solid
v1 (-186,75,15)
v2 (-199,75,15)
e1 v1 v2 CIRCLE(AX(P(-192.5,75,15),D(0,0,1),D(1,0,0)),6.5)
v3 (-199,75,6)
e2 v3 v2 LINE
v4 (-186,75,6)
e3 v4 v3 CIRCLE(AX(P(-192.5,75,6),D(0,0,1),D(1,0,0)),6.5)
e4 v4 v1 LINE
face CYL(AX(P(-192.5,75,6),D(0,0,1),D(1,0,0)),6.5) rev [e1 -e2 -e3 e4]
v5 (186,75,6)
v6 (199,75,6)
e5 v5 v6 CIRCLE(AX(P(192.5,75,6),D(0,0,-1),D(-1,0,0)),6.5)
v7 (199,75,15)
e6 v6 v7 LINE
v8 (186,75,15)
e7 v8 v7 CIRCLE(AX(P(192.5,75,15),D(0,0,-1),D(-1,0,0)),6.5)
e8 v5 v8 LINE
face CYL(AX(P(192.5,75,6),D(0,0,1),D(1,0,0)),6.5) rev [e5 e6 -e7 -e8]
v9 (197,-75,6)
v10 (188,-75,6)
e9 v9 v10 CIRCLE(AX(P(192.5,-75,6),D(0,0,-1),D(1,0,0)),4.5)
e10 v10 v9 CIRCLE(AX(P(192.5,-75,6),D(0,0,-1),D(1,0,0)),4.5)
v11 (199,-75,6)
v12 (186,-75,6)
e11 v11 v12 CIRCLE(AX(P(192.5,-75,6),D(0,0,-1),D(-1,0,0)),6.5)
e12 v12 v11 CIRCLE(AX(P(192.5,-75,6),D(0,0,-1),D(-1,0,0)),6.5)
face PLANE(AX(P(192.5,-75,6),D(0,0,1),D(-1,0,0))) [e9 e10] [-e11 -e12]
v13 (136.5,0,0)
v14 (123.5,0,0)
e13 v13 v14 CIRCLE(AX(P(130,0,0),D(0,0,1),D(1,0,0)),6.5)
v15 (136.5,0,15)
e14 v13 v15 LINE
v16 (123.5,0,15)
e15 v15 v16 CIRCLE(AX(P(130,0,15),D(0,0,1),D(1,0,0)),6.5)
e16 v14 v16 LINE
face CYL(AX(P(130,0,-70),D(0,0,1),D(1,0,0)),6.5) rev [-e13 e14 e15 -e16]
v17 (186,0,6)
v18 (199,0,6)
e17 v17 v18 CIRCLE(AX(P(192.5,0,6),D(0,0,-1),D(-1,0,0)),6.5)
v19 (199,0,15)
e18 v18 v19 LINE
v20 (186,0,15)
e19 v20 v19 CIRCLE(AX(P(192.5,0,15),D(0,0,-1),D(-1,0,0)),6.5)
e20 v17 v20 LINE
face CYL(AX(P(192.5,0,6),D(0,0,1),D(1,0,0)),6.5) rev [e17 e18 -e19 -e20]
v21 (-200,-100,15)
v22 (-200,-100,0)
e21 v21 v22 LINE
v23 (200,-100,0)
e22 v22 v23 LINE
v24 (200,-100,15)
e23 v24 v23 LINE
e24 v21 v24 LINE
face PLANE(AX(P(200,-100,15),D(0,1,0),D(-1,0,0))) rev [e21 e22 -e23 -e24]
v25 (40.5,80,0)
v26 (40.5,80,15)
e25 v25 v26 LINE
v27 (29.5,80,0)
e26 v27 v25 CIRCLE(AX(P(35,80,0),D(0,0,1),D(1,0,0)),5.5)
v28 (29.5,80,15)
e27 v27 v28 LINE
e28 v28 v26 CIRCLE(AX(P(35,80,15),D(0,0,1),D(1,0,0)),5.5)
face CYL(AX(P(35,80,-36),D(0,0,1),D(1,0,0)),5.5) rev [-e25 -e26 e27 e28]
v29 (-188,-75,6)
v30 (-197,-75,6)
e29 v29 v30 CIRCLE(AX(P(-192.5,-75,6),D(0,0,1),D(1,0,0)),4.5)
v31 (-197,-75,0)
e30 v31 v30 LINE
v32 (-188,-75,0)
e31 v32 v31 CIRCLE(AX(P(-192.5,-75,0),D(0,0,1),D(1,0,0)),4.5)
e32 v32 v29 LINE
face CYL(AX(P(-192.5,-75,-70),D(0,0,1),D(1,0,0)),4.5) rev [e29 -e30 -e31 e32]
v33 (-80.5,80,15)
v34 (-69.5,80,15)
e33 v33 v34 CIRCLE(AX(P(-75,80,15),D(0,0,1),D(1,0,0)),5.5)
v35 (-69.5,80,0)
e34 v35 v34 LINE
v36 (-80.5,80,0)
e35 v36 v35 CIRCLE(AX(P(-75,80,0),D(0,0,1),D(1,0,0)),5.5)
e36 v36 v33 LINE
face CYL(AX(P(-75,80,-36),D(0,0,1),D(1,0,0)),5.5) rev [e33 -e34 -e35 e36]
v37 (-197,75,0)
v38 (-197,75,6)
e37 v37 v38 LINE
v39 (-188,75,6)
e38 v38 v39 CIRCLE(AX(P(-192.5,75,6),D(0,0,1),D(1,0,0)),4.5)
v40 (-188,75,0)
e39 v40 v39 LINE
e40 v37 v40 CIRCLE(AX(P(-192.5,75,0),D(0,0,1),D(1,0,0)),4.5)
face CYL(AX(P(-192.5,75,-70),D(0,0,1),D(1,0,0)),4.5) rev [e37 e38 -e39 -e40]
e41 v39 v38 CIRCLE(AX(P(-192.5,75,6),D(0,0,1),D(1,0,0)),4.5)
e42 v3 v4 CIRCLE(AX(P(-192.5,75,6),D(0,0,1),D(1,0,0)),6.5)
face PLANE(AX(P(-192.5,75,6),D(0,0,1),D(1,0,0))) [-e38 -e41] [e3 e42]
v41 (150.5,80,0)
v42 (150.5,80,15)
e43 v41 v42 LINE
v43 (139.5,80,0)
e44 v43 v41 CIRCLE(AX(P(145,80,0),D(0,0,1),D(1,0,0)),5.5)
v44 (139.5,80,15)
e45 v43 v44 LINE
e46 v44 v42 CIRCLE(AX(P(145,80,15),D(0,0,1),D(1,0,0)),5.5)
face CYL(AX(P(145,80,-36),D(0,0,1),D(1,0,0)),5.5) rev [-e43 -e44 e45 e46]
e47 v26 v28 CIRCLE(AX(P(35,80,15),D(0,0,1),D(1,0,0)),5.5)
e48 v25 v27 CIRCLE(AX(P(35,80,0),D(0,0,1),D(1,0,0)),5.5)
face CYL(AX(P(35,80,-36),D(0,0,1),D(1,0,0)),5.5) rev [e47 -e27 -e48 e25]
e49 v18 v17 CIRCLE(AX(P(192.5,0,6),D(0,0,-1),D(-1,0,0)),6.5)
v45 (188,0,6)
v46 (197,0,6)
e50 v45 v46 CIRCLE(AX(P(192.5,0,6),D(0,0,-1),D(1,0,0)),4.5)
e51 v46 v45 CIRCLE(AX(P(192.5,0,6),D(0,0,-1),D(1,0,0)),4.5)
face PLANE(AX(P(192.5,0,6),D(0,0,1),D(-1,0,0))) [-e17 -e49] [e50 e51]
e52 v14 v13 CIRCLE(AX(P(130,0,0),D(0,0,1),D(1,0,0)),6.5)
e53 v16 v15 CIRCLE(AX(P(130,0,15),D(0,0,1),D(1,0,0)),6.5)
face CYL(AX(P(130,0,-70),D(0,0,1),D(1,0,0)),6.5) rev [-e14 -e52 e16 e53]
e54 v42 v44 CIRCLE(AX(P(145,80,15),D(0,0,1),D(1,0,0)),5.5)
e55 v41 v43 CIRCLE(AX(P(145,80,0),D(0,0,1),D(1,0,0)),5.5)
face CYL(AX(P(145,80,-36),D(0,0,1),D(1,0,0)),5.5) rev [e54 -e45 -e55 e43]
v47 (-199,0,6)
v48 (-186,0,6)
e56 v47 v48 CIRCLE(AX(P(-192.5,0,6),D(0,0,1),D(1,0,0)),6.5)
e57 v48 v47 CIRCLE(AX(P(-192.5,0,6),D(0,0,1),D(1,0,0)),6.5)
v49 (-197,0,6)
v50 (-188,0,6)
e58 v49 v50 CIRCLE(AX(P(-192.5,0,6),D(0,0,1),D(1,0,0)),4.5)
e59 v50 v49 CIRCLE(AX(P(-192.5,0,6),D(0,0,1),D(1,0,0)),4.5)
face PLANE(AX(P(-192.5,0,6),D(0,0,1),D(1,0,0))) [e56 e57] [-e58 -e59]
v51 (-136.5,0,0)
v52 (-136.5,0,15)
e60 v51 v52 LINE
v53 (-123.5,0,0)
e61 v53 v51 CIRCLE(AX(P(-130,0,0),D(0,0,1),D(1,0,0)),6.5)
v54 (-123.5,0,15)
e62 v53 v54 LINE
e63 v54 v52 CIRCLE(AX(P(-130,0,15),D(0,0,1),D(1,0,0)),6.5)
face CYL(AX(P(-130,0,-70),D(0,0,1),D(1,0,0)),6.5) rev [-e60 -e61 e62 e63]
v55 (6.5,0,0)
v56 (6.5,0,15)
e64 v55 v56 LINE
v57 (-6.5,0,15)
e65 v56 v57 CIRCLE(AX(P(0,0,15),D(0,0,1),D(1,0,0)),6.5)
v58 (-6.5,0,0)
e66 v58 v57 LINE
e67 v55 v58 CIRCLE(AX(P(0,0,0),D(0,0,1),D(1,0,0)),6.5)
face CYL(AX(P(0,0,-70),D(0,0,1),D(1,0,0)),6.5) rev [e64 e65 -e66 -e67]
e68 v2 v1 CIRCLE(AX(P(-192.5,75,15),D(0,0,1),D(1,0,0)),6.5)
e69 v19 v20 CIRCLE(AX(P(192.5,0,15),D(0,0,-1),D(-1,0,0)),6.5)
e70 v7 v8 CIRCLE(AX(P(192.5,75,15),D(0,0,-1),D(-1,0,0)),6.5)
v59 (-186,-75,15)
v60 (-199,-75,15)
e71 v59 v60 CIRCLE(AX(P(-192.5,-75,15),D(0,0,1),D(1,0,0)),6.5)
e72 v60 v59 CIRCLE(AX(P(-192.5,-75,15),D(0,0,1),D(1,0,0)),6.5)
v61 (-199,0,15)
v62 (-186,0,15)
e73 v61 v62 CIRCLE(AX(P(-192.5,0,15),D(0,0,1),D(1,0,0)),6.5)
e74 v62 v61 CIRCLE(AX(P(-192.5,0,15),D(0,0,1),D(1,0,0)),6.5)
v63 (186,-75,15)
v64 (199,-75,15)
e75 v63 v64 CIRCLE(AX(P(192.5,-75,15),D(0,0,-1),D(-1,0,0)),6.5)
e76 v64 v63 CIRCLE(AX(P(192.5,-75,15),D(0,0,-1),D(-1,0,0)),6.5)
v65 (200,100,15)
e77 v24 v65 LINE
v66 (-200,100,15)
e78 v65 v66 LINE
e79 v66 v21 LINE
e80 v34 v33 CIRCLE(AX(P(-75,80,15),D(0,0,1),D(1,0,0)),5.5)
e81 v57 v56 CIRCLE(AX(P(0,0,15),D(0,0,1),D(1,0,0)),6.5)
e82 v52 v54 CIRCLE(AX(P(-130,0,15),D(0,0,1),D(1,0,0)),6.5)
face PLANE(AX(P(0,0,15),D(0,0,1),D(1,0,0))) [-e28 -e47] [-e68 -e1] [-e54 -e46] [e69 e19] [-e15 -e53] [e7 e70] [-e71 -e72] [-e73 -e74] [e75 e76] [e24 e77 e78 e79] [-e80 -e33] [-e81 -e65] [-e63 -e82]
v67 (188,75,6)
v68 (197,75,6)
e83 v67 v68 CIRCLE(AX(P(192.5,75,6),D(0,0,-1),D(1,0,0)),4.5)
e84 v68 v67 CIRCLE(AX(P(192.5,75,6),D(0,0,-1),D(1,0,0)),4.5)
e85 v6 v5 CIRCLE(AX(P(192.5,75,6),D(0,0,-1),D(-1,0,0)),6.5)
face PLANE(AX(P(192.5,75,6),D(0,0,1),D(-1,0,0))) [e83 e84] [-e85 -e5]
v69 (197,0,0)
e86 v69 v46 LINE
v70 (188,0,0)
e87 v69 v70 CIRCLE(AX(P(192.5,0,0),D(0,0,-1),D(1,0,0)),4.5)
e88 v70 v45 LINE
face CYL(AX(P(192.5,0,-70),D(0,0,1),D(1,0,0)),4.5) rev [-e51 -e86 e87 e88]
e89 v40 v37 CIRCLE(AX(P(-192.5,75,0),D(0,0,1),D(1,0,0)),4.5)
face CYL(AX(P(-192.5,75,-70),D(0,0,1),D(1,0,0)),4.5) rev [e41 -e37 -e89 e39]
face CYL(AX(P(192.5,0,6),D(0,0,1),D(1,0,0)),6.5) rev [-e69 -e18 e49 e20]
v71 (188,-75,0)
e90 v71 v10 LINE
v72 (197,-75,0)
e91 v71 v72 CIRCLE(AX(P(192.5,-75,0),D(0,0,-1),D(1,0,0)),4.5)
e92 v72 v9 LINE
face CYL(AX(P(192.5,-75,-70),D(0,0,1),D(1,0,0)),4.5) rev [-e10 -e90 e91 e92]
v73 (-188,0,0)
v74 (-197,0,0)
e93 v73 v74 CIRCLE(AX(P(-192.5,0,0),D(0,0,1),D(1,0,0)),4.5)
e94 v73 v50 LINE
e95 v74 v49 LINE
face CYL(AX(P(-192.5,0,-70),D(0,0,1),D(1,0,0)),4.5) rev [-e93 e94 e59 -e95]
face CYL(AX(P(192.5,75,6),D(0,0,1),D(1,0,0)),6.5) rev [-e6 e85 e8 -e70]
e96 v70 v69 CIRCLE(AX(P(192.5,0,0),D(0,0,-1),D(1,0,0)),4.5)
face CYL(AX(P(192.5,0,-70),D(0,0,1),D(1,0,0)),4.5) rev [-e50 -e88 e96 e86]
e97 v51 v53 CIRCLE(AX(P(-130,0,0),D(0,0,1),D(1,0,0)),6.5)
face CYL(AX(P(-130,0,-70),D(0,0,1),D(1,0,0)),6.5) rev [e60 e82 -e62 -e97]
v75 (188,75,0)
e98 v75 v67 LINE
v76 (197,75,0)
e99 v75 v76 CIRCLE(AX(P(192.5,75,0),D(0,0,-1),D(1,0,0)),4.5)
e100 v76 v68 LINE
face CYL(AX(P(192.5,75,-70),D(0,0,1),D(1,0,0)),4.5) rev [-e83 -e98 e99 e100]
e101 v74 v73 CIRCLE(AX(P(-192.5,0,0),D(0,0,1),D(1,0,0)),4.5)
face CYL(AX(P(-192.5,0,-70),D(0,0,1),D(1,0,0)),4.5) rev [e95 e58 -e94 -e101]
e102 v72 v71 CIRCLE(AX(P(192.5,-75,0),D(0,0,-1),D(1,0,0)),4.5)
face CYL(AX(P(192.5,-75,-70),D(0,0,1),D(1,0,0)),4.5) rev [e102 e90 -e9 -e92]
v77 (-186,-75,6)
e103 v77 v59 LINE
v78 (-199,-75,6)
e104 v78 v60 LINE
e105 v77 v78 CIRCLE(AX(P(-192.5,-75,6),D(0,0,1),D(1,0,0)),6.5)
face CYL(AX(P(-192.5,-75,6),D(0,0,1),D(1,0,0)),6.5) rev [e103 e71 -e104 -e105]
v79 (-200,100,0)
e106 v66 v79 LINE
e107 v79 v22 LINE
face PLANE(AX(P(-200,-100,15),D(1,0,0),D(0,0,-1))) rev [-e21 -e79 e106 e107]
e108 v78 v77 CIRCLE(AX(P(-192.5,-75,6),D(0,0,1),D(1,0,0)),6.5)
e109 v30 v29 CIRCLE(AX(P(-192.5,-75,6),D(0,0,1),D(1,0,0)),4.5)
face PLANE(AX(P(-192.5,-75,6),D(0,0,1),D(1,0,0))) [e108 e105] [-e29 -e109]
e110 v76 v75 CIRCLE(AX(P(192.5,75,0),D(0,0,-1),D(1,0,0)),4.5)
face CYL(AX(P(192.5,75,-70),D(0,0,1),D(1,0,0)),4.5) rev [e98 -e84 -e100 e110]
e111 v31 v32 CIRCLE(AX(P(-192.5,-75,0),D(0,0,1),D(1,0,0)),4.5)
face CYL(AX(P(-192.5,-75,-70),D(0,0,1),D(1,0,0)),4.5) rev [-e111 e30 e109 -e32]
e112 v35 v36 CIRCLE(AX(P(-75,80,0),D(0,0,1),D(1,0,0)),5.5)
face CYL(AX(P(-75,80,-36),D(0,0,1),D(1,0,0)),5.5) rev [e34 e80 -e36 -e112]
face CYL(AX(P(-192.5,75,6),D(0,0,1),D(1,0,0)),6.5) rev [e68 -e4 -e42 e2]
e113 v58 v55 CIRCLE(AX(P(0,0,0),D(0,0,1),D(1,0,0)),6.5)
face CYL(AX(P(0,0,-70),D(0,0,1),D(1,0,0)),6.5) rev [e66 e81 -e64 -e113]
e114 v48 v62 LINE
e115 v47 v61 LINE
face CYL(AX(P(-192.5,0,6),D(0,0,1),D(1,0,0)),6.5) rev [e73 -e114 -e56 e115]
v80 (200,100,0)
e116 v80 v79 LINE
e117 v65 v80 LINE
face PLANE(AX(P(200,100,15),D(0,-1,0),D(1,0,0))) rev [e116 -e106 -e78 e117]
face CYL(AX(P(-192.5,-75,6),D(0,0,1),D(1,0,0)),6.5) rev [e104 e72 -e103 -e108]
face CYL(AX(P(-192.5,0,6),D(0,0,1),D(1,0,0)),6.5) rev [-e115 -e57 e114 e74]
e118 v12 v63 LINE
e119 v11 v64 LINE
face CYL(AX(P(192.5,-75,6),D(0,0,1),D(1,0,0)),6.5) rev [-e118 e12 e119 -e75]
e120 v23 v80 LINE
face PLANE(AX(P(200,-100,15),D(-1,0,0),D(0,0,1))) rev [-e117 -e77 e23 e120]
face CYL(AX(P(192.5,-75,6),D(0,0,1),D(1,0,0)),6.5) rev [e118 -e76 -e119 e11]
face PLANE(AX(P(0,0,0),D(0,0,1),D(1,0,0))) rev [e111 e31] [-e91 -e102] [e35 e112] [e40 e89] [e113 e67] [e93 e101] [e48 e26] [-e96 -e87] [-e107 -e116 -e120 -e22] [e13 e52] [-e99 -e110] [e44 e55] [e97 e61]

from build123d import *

# Parameters (mm, degrees)
SKETCH1_W               = 400
SKETCH1_H               = 200
BOSS_EXTRUDE1_DEPTH     = 15
SKETCH2_R               = 6.5
CUT_EXTRUDE1_DEPTH      = 9
LPATTERN1_COUNT         = 3
LPATTERN1_PITCH         = 75
MIRROR1_COPY_1_SKETCH_R = 6.5
MIRROR1_COPY_1_DEPTH    = 9
MIRROR1_COPY_2_SKETCH_R = 6.5
MIRROR1_COPY_2_DEPTH    = 9
SKETCH3_R               = 4.5
CUT_EXTRUDE2_DEPTH      = 85
LPATTERN2_COUNT         = 3
LPATTERN2_PITCH         = 75
MIRROR2_COPY_1_SKETCH_R = 4.5
MIRROR2_COPY_1_DEPTH    = 85
MIRROR2_COPY_2_SKETCH_R = 4.5
MIRROR2_COPY_2_DEPTH    = 85
SKETCH4_R               = 6.5
CUT_EXTRUDE3_DEPTH      = 85
LPATTERN3_COUNT         = 3
LPATTERN3_PITCH         = 130
SKETCH5_R               = 5.5
CUT_EXTRUDE4_DEPTH      = 51
LPATTERN4_COUNT         = 3
LPATTERN4_PITCH         = 110


with BuildPart() as part:
    # Sketch1 → Boss-Extrude1 (new body)
    with BuildSketch(Plane.XY):
        Rectangle(SKETCH1_W, SKETCH1_H)
    extrude(amount=BOSS_EXTRUDE1_DEPTH)

    # Sketch2 → Cut-Extrude1 (cut)
    with BuildSketch(Plane.XY.offset(15)):
        with Locations((-192.5, 75)):
            Circle(SKETCH2_R)
    cut_extrude1 = extrude(amount=-CUT_EXTRUDE1_DEPTH, mode=Mode.SUBTRACT)

    # LPattern1: Cut-Extrude1 ×3
    with Locations(*[(0, -i * LPATTERN1_PITCH, 0) for i in range(1, LPATTERN1_COUNT)]):
        add(cut_extrude1, mode=Mode.SUBTRACT)

    # Mirror1: Cut-Extrude1 across plane
    add(cut_extrude1.mirror(Plane(origin=(0, 0, 0), x_dir=(0, 0, 1), z_dir=(1, 0, 0))), mode=Mode.SUBTRACT)

    # Mirror1 copy 1 sketch → Mirror1 copy 1 (cut)
    with BuildSketch(Plane(origin=(0, -75, 15), x_dir=(-1, 0, 0), z_dir=(0, 0, 1))):
        with Locations((-192.5, -75)):
            Circle(MIRROR1_COPY_1_SKETCH_R)
    extrude(amount=-MIRROR1_COPY_1_DEPTH, mode=Mode.SUBTRACT)

    # Mirror1 copy 2 sketch → Mirror1 copy 2 (cut)
    with BuildSketch(Plane(origin=(0, -150, 15), x_dir=(-1, 0, 0), z_dir=(0, 0, 1))):
        with Locations((-192.5, -75)):
            Circle(MIRROR1_COPY_2_SKETCH_R)
    extrude(amount=-MIRROR1_COPY_2_DEPTH, mode=Mode.SUBTRACT)

    # Sketch3 → Cut-Extrude2 (cut)
    with BuildSketch(Plane.XY.offset(15)):
        with Locations((-192.5, 75)):
            Circle(SKETCH3_R)
    cut_extrude2 = extrude(amount=-CUT_EXTRUDE2_DEPTH, mode=Mode.SUBTRACT)

    # LPattern2: Cut-Extrude2 ×3
    with Locations(*[(0, -i * LPATTERN2_PITCH, 0) for i in range(1, LPATTERN2_COUNT)]):
        add(cut_extrude2, mode=Mode.SUBTRACT)

    # Mirror2: Cut-Extrude2 across plane
    add(cut_extrude2.mirror(Plane(origin=(0, 0, 0), x_dir=(0, 0, 1), z_dir=(1, 0, 0))), mode=Mode.SUBTRACT)

    # Mirror2 copy 1 sketch → Mirror2 copy 1 (cut)
    with BuildSketch(Plane(origin=(0, -75, 15), x_dir=(-1, 0, 0), z_dir=(0, 0, 1))):
        with Locations((-192.5, -75)):
            Circle(MIRROR2_COPY_1_SKETCH_R)
    extrude(amount=-MIRROR2_COPY_1_DEPTH, mode=Mode.SUBTRACT)

    # Mirror2 copy 2 sketch → Mirror2 copy 2 (cut)
    with BuildSketch(Plane(origin=(0, -150, 15), x_dir=(-1, 0, 0), z_dir=(0, 0, 1))):
        with Locations((-192.5, -75)):
            Circle(MIRROR2_COPY_2_SKETCH_R)
    extrude(amount=-MIRROR2_COPY_2_DEPTH, mode=Mode.SUBTRACT)

    # Sketch4 → Cut-Extrude3 (cut)
    with BuildSketch(Plane.XY.offset(15)):
        with Locations((-130, 0)):
            Circle(SKETCH4_R)
    cut_extrude3 = extrude(amount=-CUT_EXTRUDE3_DEPTH, mode=Mode.SUBTRACT)

    # LPattern3: Cut-Extrude3 ×3
    with Locations(*[(i * LPATTERN3_PITCH, 0, 0) for i in range(1, LPATTERN3_COUNT)]):
        add(cut_extrude3, mode=Mode.SUBTRACT)

    # Sketch5 → Cut-Extrude4 (cut)
    with BuildSketch(Plane.XY.offset(15)):
        with Locations((-75, 80)):
            Circle(SKETCH5_R)
    cut_extrude4 = extrude(amount=-CUT_EXTRUDE4_DEPTH, mode=Mode.SUBTRACT)

    # LPattern4: Cut-Extrude4 ×3
    with Locations(*[(i * LPATTERN4_PITCH, 0, 0) for i in range(1, LPATTERN4_COUNT)]):
        add(cut_extrude4, mode=Mode.SUBTRACT)


solid = part.part
